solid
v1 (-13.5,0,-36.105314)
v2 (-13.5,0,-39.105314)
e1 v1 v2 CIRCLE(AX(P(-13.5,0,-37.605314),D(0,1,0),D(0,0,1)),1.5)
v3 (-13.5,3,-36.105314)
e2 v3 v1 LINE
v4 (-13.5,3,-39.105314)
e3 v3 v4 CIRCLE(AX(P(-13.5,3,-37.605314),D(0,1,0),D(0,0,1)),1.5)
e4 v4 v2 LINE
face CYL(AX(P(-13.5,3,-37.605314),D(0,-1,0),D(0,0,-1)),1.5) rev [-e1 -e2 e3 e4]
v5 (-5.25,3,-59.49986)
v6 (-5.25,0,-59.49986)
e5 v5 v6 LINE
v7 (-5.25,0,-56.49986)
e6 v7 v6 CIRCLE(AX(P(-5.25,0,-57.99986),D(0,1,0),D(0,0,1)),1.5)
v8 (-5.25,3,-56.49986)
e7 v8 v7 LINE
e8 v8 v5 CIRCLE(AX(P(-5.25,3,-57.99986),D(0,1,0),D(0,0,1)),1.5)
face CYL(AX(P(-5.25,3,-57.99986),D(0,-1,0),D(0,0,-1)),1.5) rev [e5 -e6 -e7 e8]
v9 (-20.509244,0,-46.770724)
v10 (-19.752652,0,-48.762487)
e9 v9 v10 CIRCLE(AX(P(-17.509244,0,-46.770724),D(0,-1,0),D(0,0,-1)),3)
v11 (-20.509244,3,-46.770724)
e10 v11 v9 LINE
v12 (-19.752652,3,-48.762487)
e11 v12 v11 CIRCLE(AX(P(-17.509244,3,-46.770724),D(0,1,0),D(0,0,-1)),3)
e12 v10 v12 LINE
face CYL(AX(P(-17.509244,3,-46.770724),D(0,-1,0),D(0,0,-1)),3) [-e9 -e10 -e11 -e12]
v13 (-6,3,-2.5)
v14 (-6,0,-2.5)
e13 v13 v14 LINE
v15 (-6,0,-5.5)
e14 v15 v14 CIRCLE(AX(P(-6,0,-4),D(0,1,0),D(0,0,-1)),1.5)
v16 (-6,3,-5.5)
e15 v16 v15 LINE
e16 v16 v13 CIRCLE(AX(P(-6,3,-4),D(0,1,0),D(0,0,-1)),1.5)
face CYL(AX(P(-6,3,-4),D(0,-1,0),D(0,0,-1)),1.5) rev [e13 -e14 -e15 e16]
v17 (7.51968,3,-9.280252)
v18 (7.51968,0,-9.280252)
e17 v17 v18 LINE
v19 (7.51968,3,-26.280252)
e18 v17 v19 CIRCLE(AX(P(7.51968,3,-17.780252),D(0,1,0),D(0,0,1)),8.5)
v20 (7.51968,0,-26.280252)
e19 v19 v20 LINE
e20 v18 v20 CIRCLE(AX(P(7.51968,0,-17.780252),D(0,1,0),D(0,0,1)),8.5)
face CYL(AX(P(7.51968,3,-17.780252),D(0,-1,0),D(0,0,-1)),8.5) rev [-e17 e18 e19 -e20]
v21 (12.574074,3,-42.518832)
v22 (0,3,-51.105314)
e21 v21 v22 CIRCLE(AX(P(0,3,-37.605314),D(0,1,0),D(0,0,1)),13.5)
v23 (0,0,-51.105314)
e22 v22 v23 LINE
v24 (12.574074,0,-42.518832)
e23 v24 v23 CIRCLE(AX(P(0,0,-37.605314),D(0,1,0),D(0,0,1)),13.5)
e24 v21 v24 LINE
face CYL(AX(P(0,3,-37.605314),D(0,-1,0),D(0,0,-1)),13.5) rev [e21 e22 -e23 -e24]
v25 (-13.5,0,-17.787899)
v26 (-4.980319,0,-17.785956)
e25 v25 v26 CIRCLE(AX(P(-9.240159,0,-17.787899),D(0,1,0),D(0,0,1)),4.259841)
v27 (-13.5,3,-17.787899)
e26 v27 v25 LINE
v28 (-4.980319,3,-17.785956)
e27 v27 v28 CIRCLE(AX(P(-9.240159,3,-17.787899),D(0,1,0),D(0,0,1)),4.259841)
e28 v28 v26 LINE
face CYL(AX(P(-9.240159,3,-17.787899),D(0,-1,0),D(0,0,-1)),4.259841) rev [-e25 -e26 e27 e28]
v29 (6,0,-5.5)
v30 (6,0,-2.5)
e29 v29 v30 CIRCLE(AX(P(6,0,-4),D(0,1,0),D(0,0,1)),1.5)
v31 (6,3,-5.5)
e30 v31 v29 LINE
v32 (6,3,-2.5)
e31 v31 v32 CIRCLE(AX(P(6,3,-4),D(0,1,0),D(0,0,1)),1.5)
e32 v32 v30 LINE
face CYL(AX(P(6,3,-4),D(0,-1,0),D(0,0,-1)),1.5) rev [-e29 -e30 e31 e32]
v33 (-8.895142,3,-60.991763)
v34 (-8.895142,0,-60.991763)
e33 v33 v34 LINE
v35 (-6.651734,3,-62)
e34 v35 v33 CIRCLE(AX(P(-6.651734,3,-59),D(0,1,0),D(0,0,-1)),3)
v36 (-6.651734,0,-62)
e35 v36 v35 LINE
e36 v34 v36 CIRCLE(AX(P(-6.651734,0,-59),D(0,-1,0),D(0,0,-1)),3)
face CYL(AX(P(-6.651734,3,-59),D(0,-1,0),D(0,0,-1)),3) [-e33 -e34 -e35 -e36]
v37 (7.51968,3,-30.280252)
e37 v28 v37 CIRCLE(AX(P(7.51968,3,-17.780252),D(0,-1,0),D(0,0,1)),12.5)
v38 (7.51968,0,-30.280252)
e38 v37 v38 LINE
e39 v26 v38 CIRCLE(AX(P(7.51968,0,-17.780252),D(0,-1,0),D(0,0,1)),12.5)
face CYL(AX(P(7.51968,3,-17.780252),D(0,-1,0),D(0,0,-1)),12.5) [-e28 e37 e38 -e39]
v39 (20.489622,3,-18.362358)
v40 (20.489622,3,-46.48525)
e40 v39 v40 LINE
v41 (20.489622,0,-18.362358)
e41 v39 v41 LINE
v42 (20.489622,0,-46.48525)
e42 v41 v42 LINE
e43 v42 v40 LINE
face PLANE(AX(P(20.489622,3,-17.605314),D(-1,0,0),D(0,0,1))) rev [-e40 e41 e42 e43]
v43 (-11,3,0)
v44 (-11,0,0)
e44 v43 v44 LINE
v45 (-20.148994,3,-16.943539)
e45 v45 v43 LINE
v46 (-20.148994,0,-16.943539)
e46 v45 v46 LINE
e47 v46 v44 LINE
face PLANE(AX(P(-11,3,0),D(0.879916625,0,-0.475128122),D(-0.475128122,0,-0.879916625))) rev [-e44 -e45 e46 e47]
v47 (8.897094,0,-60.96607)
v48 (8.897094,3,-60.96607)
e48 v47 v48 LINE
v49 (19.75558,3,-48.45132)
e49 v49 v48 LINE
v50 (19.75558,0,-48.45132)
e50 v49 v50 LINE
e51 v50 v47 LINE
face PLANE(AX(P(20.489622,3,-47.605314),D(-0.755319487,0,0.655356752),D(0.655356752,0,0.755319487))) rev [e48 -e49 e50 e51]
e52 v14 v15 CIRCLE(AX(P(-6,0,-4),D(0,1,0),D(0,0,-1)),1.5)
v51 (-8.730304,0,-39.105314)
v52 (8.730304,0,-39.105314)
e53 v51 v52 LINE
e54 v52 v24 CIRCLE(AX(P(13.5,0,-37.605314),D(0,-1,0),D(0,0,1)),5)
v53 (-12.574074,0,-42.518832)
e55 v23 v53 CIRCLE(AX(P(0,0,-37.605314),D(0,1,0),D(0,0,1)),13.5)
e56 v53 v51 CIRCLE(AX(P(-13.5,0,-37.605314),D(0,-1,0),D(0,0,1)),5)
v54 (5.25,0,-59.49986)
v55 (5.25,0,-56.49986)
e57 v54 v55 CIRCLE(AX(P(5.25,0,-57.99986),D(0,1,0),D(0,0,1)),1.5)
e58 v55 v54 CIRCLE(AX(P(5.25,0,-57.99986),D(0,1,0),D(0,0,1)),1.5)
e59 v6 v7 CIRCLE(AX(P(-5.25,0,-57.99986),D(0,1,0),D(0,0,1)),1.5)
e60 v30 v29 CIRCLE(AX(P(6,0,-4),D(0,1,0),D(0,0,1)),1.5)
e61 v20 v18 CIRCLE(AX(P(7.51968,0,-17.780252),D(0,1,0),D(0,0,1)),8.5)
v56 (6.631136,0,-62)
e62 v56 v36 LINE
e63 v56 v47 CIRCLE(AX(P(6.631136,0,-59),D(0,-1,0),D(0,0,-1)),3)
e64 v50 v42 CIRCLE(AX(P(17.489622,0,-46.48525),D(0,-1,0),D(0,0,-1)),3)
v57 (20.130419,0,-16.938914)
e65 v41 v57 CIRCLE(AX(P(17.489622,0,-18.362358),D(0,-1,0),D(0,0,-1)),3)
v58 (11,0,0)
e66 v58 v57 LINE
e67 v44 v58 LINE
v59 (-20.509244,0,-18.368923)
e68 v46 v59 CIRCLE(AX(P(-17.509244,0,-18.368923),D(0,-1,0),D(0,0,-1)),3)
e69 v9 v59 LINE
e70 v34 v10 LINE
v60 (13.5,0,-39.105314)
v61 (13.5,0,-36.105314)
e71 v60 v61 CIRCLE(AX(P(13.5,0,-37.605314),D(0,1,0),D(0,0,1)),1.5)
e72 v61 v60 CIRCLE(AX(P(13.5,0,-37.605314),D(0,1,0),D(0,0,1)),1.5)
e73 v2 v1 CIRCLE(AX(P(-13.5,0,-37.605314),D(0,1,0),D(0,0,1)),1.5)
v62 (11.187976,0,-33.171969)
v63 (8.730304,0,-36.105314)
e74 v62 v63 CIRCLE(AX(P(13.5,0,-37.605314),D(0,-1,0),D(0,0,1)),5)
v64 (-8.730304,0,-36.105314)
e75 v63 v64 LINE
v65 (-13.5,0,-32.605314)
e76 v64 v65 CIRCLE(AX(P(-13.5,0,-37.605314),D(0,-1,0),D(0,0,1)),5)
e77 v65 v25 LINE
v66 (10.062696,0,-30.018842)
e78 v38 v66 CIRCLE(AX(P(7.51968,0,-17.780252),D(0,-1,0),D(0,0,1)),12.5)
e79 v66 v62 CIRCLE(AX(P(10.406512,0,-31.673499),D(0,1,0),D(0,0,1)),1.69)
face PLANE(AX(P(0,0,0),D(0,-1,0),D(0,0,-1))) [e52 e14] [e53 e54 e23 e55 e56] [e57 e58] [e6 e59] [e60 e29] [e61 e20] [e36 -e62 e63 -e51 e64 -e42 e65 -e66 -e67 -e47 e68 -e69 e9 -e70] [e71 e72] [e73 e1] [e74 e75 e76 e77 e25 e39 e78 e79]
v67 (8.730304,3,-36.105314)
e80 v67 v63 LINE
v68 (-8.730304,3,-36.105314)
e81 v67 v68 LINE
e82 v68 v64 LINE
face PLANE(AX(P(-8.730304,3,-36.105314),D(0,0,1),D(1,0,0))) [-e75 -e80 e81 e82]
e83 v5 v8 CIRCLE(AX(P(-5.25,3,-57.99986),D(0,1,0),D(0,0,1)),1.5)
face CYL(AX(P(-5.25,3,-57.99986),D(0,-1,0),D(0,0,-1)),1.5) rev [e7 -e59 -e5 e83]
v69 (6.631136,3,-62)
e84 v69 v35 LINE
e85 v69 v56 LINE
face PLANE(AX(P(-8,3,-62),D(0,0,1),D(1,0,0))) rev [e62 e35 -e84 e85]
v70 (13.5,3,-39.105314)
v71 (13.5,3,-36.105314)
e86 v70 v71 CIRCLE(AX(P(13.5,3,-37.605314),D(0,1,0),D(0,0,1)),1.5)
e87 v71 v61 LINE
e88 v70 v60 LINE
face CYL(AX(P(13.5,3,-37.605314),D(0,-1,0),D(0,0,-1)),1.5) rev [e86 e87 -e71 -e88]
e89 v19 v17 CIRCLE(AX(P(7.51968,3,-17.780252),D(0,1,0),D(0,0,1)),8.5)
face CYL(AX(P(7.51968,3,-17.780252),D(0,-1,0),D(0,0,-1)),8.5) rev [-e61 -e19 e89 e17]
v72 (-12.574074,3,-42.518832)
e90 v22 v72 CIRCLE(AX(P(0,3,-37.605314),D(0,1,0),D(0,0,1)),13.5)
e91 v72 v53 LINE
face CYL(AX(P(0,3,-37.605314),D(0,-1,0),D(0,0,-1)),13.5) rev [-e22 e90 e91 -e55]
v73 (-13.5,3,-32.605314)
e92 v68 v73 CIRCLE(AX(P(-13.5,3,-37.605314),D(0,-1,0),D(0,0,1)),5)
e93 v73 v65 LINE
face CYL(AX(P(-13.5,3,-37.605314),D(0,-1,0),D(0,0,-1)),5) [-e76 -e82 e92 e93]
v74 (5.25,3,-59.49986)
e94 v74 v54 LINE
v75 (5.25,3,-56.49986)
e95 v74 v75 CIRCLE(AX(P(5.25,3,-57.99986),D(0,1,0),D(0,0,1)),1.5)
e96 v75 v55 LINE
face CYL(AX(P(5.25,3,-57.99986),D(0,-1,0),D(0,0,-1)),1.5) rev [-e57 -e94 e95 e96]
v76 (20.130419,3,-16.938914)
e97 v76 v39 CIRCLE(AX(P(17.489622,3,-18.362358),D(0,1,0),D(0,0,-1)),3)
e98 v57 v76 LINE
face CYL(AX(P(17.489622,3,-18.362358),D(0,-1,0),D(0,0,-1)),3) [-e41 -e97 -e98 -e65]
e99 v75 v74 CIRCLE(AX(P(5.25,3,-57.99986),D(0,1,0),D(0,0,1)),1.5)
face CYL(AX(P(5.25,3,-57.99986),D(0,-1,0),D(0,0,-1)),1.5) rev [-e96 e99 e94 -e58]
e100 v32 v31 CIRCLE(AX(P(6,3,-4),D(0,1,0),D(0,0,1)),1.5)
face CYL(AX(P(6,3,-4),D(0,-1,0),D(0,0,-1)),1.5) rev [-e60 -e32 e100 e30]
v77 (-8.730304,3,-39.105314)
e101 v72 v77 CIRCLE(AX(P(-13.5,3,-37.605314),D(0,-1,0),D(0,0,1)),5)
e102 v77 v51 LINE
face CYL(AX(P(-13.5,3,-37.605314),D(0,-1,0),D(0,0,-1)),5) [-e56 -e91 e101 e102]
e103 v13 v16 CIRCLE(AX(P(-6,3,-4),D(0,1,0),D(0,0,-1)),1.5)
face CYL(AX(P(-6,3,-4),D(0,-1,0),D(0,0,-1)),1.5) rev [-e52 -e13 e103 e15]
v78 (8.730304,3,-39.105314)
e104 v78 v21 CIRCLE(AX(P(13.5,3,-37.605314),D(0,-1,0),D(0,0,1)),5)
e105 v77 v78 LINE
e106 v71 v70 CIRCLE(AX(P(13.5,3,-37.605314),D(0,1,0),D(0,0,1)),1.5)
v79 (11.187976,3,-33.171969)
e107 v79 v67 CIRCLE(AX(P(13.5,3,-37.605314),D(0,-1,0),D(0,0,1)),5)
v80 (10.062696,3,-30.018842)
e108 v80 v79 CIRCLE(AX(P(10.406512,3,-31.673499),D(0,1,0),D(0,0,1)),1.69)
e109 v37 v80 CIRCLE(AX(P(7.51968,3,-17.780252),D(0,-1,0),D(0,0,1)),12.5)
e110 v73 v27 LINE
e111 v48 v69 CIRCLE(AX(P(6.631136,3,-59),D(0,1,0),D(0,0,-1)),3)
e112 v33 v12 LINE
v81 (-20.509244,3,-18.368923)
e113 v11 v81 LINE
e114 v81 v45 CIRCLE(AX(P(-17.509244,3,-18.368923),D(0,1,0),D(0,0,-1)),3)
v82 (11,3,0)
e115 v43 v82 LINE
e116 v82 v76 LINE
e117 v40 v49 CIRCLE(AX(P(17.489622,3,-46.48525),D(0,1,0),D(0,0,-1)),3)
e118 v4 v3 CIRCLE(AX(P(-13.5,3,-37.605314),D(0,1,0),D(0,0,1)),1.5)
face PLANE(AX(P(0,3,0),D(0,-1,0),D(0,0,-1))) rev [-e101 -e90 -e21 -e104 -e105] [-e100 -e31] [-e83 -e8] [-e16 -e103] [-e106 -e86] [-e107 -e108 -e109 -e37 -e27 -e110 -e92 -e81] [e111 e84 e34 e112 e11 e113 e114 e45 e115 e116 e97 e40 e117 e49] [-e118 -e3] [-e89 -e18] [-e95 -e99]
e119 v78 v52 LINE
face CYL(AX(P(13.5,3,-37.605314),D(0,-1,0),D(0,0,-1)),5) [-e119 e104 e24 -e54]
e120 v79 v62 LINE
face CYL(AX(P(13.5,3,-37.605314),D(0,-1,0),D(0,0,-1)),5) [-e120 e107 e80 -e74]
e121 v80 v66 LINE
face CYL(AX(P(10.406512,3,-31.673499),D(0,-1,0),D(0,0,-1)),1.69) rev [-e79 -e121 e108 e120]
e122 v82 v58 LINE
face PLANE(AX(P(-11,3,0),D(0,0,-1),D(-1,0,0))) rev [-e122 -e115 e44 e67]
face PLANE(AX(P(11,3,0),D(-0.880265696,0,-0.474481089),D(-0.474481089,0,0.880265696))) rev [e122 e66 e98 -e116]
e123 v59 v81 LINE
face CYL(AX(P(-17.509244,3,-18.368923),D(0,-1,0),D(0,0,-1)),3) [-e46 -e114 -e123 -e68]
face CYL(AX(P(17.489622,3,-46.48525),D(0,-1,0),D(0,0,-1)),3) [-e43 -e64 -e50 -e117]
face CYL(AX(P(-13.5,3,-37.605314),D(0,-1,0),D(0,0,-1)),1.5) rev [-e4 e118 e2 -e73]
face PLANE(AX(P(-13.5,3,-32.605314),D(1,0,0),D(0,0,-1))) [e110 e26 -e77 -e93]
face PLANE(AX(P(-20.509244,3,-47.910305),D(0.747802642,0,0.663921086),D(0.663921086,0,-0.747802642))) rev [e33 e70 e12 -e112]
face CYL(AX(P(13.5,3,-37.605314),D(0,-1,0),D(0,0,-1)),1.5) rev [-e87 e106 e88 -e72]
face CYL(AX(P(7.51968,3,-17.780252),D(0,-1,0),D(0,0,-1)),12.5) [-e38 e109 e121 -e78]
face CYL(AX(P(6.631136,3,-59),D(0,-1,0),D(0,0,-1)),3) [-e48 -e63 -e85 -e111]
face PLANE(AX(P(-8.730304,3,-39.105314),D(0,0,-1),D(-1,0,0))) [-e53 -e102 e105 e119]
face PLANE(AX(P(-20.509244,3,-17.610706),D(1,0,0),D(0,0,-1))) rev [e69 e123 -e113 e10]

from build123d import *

# Parameters (mm, degrees)
SKETCH1_R           = 8.5
SKETCH1_R_2         = 1.5
BOSS_EXTRUDE1_DEPTH = 3
FILLET1_R           = 3


with BuildPart() as part:
    # Sketch1 → Boss-Extrude1 (new body)
    with BuildSketch(Plane(origin=(0, 0, 0), x_dir=(1, 0, 0), z_dir=(0, 1, 0))):
        Polygon((-11, 0), (11, 0), (20.489621783, 17.605313925), (20.489621783, 47.605313925), (8, 62), (-8, 62), (-20.509243816, 47.910305032), (-20.509243816, 17.610706132), align=None)
        with Locations(Location((7.519679741, 17.780252273, 0), (0, 0, 270))):
            Circle(SKETCH1_R, mode=Mode.SUBTRACT)
        with Locations(Location((6, 4, 0), (0, 0, 270))):
            Circle(SKETCH1_R_2, mode=Mode.SUBTRACT)
        with Locations(Location((-6, 4, 0), (0, 0, 90))):
            Circle(SKETCH1_R_2, mode=Mode.SUBTRACT)
        with Locations(Location((-5.25, 57.999859765, 0), (0, 0, 270))):
            Circle(SKETCH1_R_2, mode=Mode.SUBTRACT)
        with Locations(Location((5.25, 57.999859765, 0), (0, 0, 270))):
            Circle(SKETCH1_R_2, mode=Mode.SUBTRACT)
        with Locations(Location((-13.5, 37.605313925, 0), (0, 0, 270))):
            Circle(SKETCH1_R_2, mode=Mode.SUBTRACT)
        with Locations(Location((13.5, 37.605313925, 0), (0, 0, 270))):
            Circle(SKETCH1_R_2, mode=Mode.SUBTRACT)
        with BuildLine():
            Line((-8.730303993, 39.105313925), (8.730303993, 39.105313925))
            ThreePointArc((8.730303993, 39.105313925), (10.179901517, 41.34388933), (12.574074074, 42.518832133))
            ThreePointArc((12.574074074, 42.518832133), (0, 51.105313925), (-12.574074074, 42.518832133))
            ThreePointArc((-12.574074074, 42.518832133), (-10.179901517, 41.34388933), (-8.730303993, 39.105313925))
        make_face(mode=Mode.SUBTRACT)
        with BuildLine():
            Line((-8.730303993, 36.105313925), (8.730303993, 36.105313925))
            ThreePointArc((8.730303993, 36.105313925), (9.667400631, 34.394210987), (11.187975781, 33.171969363))
            ThreePointArc((11.187975781, 33.171969363), (11.998189223, 31.105465162), (10.062695821, 30.018841621))
            ThreePointArc((10.062695821, 30.018841621), (-0.366780245, 27.478383479), (-4.980318958, 17.785955551))
            ThreePointArc((-4.980318958, 17.785955551), (-9.241131059, 13.528058523), (-13.5, 17.787899155))
            Line((-13.5, 17.787899155), (-13.5, 32.605313925))
            ThreePointArc((-13.5, 32.605313925), (-10.541960108, 33.574185051), (-8.730303993, 36.105313925))
        make_face(mode=Mode.SUBTRACT)
    extrude(amount=BOSS_EXTRUDE1_DEPTH)

    # Fillet1
    fillet1_edges = [part.edges().sort_by_distance(p)[0] for p in [
        (-20.509243816, 1.5, -17.610706132),
        (-20.509243816, 1.5, -47.910305032),
        (-8, 1.5, -62),
        (8, 1.5, -62),
        (20.489621783, 1.5, -47.605313925),
        (20.489621783, 1.5, -17.605313925),
    ]]
    fillet(fillet1_edges, radius=FILLET1_R)


solid = part.part
